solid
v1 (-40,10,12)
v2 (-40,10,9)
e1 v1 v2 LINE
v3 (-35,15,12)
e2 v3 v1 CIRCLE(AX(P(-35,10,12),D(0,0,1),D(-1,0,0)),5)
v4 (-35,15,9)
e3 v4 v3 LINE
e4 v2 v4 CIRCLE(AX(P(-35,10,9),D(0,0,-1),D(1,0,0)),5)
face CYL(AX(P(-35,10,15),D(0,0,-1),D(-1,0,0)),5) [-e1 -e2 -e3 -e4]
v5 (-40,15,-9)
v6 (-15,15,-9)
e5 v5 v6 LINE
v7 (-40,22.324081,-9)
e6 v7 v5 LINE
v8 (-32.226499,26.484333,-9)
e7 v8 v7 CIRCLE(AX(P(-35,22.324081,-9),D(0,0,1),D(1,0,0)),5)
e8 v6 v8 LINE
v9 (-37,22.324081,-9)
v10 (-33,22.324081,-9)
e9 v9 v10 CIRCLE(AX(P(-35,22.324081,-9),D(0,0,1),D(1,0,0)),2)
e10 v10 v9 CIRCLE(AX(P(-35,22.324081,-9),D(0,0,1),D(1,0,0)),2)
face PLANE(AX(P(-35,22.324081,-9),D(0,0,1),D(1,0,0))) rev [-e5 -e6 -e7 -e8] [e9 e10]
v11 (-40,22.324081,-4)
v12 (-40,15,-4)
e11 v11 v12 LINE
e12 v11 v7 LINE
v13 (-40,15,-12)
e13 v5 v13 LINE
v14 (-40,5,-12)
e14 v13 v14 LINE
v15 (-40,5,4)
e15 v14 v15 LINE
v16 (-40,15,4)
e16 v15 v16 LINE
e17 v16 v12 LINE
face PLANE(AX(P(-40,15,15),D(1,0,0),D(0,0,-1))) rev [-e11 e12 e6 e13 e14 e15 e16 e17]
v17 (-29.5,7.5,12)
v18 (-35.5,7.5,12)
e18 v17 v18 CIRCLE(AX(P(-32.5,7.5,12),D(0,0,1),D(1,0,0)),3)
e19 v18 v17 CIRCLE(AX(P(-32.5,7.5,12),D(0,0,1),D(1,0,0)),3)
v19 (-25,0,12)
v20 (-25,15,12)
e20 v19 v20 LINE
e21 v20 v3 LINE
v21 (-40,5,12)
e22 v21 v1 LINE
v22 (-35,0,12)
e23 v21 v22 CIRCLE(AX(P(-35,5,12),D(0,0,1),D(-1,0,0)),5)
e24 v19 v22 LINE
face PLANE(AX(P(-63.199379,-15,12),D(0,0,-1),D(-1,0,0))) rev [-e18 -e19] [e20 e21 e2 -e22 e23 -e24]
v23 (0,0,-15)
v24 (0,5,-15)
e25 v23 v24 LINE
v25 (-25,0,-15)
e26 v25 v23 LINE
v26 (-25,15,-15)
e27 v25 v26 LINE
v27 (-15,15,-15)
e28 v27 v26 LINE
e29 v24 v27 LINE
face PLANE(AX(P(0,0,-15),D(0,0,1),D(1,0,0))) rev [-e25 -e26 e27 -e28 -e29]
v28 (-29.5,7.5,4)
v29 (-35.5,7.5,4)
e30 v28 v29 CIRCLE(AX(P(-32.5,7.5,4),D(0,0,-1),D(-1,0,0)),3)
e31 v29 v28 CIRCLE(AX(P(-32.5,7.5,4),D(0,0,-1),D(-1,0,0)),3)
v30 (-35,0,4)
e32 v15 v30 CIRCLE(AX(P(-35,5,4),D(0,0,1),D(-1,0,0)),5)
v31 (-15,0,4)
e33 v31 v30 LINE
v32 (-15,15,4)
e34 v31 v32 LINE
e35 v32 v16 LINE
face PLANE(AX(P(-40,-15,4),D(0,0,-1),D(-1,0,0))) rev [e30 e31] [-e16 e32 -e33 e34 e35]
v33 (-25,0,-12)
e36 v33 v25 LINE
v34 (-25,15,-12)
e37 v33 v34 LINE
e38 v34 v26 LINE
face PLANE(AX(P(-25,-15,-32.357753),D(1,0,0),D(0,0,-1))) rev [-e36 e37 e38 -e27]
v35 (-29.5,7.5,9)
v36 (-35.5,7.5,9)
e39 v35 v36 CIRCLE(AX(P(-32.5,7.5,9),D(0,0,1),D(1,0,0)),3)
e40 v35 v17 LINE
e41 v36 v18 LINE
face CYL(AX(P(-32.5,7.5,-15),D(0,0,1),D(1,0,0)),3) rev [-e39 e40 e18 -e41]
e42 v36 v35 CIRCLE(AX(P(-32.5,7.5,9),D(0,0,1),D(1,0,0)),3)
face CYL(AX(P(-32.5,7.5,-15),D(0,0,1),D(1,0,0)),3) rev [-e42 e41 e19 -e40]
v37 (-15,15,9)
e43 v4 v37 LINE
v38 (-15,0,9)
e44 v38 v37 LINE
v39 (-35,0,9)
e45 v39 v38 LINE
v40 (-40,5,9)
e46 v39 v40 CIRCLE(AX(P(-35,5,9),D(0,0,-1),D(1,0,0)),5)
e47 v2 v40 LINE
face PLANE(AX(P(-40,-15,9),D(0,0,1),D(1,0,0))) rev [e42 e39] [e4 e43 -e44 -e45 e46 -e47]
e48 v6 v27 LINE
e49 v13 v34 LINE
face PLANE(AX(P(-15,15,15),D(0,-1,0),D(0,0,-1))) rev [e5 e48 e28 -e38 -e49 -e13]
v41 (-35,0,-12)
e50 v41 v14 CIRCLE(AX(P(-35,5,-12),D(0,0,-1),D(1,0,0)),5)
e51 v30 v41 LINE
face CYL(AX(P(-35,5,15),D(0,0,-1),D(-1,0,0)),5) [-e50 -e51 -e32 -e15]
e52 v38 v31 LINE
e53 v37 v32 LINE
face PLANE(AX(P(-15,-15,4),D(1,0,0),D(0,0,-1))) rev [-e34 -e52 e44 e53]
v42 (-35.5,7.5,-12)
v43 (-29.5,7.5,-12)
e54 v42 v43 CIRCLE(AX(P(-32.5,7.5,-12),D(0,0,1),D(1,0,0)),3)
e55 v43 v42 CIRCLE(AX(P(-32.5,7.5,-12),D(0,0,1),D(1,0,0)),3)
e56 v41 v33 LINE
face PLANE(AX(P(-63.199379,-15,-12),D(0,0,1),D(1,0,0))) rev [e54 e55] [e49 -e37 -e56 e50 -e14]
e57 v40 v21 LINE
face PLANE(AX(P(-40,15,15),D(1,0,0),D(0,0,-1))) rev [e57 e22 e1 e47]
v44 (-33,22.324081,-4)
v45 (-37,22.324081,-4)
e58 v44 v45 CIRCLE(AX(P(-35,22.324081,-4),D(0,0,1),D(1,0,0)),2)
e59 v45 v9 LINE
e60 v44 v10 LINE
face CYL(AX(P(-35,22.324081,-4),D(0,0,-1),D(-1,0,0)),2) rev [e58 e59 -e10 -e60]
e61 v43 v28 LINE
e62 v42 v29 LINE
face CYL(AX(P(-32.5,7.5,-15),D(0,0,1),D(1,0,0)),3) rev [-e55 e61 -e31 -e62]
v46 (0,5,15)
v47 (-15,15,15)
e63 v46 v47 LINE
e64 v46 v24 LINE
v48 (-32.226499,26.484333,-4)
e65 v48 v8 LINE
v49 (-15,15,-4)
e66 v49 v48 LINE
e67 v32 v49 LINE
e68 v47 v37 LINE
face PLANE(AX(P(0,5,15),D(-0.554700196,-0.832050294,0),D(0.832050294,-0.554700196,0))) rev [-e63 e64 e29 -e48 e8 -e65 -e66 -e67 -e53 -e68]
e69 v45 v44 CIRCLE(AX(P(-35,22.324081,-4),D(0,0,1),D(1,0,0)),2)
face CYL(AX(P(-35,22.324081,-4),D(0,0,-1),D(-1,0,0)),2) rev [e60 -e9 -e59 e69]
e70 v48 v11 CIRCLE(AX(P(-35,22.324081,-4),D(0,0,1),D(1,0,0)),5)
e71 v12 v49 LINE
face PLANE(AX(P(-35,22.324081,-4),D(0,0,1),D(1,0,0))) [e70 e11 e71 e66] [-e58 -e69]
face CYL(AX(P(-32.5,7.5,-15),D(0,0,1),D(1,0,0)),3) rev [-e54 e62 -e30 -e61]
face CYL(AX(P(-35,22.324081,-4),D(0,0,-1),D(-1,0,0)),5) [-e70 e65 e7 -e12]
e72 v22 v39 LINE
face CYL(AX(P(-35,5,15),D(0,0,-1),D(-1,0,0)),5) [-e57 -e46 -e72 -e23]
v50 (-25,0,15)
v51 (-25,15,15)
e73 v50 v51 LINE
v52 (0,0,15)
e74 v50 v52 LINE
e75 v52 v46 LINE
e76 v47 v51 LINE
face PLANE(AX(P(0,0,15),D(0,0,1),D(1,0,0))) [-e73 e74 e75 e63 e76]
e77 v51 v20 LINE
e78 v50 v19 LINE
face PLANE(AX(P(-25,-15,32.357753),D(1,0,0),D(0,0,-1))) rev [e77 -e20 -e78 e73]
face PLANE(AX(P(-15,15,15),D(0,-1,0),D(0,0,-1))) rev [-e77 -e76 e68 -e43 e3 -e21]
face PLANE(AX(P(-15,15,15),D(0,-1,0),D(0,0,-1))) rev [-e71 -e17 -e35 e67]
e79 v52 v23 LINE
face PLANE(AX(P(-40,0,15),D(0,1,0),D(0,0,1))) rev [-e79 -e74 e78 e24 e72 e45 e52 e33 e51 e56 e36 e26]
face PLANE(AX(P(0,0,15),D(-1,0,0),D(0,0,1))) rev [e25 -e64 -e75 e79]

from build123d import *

# Parameters (mm, degrees)
BOSS_EXTRUDE1_DEPTH = 15
SKETCH2_W           = 38.199379203
SKETCH2_H           = 20.357752988
CUT_EXTRUDE1_DEPTH  = 30
SKETCH3_W           = 25
SKETCH3_H           = 5
CUT_EXTRUDE2_DEPTH  = 30
BOSS_EXTRUDE3_START = 6
SKETCH4_R           = 2
BOSS_EXTRUDE3_DEPTH = 5
SKETCH5_R           = 3
CUT_EXTRUDE3_DEPTH  = 27
FILLET1_R           = 5
FILLET2_R           = 5


with BuildPart() as part:
    # Sketch1 → Boss-Extrude1 (new, symmetric)
    with BuildSketch(Plane.XY):
        Polygon((0, 0), (0, 5), (-15, 15), (-40, 15), (-40, 0), align=None)
    extrude(amount=BOSS_EXTRUDE1_DEPTH, both=True)

    # Sketch2 → Cut-Extrude1 (cut)
    with BuildSketch(Plane(origin=(0, 15, 0), x_dir=(1, 0, 0), z_dir=(0, 1, 0))):
        with Locations((-44.099689602, 22.178876494)):
            Rectangle(SKETCH2_W, SKETCH2_H)
        with Locations((-44.099689602, -22.178876494)):
            Rectangle(SKETCH2_W, SKETCH2_H)
    extrude(amount=-CUT_EXTRUDE1_DEPTH, mode=Mode.SUBTRACT)

    # Sketch3 → Cut-Extrude2 (cut)
    with BuildSketch(Plane(origin=(0, 15, 0), x_dir=(1, 0, 0), z_dir=(0, 1, 0))):
        with Locations((-27.5, -6.5)):
            Rectangle(SKETCH3_W, SKETCH3_H)
    extrude(amount=-CUT_EXTRUDE2_DEPTH, mode=Mode.SUBTRACT)

    # Sketch4 → Boss-Extrude3 (add)
    with BuildSketch(Plane.XY.offset(-15).offset(BOSS_EXTRUDE3_START)):
        with BuildLine():
            Line((-15, 15), (-32.226499019, 26.484332679))
            ThreePointArc((-32.226499019, 26.484332679), (-37.359289628, 26.732454201), (-40, 22.324081208))
            Line((-40, 22.324081208), (-40, 15))
            Line((-40, 15), (-15, 15))
        make_face()
        with Locations((-35, 22.324081208)):
            Circle(SKETCH4_R, mode=Mode.SUBTRACT)
    extrude(amount=BOSS_EXTRUDE3_DEPTH)

    # Sketch5 → Cut-Extrude3 (cut)
    with BuildSketch(Plane.XY.offset(12)):
        with Locations((-32.5, 7.5)):
            Circle(SKETCH5_R)
    extrude(amount=-CUT_EXTRUDE3_DEPTH, mode=Mode.SUBTRACT)

    # Fillet1
    fillet1_edges = [part.edges().sort_by_distance(p)[0] for p in [
        (-40, 0, 10.5),
        (-40, 15, 10.5),
    ]]
    fillet(fillet1_edges, radius=FILLET1_R)

    # Fillet2
    fillet2_edges = [part.edges().sort_by_distance(p)[0] for p in [
        (-40, 0, -4),
    ]]
    fillet(fillet2_edges, radius=FILLET2_R)


solid = part.part
